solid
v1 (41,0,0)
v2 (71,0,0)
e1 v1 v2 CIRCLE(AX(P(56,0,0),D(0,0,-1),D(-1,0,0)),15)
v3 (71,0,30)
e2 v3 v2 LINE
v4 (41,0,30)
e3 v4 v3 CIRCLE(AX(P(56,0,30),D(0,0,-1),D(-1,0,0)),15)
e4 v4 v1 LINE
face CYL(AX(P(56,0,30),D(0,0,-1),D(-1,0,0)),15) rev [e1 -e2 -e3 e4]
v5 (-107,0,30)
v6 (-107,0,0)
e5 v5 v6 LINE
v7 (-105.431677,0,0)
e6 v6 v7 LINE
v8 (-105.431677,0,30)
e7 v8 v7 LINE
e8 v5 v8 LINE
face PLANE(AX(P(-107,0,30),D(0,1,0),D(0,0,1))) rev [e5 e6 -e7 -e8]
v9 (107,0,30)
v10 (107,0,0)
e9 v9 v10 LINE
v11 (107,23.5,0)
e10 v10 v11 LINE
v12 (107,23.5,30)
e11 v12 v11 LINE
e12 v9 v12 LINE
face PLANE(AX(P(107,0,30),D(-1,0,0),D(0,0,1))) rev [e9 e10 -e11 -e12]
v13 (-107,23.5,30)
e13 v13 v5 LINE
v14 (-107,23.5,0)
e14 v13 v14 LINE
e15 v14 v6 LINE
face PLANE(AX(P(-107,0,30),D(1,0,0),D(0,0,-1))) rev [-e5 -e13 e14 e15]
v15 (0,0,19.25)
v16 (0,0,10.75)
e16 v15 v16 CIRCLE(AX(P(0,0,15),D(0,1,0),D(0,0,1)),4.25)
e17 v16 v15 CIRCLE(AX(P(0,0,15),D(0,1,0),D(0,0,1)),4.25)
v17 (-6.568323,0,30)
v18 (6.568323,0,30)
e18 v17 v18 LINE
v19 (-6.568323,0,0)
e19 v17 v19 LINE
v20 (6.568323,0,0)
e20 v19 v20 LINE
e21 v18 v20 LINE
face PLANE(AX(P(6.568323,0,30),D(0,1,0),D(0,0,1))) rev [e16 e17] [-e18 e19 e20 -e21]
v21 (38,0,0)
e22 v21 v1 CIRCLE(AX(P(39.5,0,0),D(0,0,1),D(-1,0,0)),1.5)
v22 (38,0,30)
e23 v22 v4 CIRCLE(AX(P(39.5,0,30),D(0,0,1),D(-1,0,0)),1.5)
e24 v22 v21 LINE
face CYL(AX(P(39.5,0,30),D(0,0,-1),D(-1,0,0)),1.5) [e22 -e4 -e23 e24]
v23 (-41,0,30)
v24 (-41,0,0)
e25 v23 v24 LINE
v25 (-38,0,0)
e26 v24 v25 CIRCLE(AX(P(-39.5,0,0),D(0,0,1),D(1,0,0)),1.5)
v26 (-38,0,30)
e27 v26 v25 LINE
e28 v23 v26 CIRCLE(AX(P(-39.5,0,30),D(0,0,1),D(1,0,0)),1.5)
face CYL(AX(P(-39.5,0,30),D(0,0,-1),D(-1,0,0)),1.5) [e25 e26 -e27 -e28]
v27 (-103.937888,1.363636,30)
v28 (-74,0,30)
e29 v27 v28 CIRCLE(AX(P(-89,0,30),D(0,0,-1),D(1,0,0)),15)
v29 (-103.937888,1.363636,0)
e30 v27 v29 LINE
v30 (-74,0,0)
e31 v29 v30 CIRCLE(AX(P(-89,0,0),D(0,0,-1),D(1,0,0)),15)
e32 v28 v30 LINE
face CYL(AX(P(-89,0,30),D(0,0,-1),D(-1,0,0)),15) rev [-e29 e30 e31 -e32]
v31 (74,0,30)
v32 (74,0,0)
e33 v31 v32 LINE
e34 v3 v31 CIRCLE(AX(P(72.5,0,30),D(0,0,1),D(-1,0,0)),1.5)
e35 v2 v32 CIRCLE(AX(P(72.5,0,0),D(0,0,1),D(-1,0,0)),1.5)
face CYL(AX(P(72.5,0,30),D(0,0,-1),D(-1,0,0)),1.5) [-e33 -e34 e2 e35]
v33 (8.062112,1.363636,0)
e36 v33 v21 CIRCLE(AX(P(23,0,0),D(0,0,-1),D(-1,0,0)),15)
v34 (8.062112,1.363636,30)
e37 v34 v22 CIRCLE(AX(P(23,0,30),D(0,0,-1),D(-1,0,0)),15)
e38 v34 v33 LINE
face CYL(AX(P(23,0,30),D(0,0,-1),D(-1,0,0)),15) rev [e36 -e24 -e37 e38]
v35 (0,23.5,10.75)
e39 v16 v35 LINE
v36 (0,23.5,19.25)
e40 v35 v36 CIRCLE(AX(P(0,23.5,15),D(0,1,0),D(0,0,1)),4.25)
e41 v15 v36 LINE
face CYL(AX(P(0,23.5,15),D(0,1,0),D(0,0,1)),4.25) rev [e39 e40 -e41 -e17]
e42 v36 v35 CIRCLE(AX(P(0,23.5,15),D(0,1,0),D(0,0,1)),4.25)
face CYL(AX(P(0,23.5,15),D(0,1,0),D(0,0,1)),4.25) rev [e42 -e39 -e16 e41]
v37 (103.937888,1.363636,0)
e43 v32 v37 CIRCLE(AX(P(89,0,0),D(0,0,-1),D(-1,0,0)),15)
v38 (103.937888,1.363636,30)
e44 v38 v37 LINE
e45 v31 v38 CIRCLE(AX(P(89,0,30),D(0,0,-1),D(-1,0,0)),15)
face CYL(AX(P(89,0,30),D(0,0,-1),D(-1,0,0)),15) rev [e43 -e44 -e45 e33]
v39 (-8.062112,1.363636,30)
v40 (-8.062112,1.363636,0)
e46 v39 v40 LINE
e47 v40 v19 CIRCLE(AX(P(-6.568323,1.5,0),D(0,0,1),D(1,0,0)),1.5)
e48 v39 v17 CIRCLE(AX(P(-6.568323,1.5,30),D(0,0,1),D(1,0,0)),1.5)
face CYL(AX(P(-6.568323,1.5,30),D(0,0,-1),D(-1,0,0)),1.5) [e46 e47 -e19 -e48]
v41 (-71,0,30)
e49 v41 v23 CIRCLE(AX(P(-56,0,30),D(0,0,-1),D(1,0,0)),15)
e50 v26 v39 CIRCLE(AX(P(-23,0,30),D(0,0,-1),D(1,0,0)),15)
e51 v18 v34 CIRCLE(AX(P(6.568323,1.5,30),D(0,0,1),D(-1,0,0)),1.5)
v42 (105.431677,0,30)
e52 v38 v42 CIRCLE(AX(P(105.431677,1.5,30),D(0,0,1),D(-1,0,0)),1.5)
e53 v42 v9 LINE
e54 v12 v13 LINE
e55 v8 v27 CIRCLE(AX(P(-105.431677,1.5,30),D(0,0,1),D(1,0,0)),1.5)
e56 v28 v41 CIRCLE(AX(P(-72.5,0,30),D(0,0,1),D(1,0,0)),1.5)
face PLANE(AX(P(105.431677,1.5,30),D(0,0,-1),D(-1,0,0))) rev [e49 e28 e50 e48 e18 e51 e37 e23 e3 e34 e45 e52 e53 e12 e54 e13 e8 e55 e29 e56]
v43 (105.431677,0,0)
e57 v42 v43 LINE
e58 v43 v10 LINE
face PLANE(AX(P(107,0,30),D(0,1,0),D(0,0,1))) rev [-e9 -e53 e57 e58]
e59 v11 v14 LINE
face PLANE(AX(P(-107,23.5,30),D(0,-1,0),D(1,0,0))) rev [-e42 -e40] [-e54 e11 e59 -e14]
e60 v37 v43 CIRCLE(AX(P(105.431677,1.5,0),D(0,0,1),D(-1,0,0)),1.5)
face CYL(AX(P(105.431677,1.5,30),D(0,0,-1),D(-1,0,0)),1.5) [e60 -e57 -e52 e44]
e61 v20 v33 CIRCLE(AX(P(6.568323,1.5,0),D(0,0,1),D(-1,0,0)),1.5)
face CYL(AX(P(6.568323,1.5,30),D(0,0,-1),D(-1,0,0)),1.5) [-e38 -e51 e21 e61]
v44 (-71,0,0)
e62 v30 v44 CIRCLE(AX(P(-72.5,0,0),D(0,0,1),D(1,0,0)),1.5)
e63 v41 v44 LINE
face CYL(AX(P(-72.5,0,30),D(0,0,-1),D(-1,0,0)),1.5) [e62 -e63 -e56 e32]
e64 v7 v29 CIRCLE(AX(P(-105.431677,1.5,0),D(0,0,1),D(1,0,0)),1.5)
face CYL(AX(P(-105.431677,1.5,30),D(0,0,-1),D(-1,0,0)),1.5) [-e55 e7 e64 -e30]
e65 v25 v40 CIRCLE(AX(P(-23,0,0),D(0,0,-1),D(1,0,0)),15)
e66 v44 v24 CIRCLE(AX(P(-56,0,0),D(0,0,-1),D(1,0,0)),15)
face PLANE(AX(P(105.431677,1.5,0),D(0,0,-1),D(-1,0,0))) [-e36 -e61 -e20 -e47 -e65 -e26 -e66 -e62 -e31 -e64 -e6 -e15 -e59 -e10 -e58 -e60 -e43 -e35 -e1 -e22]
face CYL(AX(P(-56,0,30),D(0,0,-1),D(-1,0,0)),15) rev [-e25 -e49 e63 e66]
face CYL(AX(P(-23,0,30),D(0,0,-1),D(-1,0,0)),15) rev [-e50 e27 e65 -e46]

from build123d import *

# Parameters (mm, degrees)
BOSS_EXTRUDE1_DEPTH = 30
M10_TAPPED_HOLE1_D  = 8.5


with BuildPart() as part:
    # Sketch1 → Boss-Extrude1 (new body)
    with BuildSketch(Plane.XY):
        with BuildLine():
            Line((-107, 0), (-107, 23.5))
            Line((-107, 23.5), (107, 23.5))
            Line((107, 23.5), (107, 0))
            Line((107, 0), (105.431676725, 0))
            ThreePointArc((105.431676725, 0), (104.420376931, 0.392176581), (103.937887932, 1.363636364))
            ThreePointArc((103.937887932, 1.363636364), (88.317474901, 14.984463937), (74, 0))
            ThreePointArc((74, 0), (72.5, -1.5), (71, 0))
            ThreePointArc((71, 0), (56, 15), (41, 0))
            ThreePointArc((41, 0), (39.5, -1.5), (38, 0))
            ThreePointArc((38, 0), (23.682525099, 14.984463937), (8.062112068, 1.363636364))
            ThreePointArc((8.062112068, 1.363636364), (7.579623069, 0.392176581), (6.568323275, 0))
            Line((6.568323275, 0), (-6.568323275, 0))
            ThreePointArc((-6.568323275, 0), (-7.579623069, 0.392176581), (-8.062112068, 1.363636364))
            ThreePointArc((-8.062112068, 1.363636364), (-23.682525099, 14.984463937), (-38, 0))
            ThreePointArc((-38, 0), (-39.5, -1.5), (-41, 0))
            ThreePointArc((-41, 0), (-56, 15), (-71, 0))
            ThreePointArc((-71, 0), (-72.5, -1.5), (-74, 0))
            ThreePointArc((-74, 0), (-88.317474901, 14.984463937), (-103.937887932, 1.363636364))
            ThreePointArc((-103.937887932, 1.363636364), (-104.420376931, 0.392176581), (-105.431676725, 0))
            Line((-105.431676725, 0), (-107, 0))
        make_face()
    extrude(amount=BOSS_EXTRUDE1_DEPTH)

    # M10 Tapped Hole1 (through all)
    with Locations(Plane(origin=(0, 23.5, 0), x_dir=(-1, 0, 0), z_dir=(0, 1, 0))):
        with Locations((0, 15)):
            Hole(M10_TAPPED_HOLE1_D / 2)


solid = part.part
